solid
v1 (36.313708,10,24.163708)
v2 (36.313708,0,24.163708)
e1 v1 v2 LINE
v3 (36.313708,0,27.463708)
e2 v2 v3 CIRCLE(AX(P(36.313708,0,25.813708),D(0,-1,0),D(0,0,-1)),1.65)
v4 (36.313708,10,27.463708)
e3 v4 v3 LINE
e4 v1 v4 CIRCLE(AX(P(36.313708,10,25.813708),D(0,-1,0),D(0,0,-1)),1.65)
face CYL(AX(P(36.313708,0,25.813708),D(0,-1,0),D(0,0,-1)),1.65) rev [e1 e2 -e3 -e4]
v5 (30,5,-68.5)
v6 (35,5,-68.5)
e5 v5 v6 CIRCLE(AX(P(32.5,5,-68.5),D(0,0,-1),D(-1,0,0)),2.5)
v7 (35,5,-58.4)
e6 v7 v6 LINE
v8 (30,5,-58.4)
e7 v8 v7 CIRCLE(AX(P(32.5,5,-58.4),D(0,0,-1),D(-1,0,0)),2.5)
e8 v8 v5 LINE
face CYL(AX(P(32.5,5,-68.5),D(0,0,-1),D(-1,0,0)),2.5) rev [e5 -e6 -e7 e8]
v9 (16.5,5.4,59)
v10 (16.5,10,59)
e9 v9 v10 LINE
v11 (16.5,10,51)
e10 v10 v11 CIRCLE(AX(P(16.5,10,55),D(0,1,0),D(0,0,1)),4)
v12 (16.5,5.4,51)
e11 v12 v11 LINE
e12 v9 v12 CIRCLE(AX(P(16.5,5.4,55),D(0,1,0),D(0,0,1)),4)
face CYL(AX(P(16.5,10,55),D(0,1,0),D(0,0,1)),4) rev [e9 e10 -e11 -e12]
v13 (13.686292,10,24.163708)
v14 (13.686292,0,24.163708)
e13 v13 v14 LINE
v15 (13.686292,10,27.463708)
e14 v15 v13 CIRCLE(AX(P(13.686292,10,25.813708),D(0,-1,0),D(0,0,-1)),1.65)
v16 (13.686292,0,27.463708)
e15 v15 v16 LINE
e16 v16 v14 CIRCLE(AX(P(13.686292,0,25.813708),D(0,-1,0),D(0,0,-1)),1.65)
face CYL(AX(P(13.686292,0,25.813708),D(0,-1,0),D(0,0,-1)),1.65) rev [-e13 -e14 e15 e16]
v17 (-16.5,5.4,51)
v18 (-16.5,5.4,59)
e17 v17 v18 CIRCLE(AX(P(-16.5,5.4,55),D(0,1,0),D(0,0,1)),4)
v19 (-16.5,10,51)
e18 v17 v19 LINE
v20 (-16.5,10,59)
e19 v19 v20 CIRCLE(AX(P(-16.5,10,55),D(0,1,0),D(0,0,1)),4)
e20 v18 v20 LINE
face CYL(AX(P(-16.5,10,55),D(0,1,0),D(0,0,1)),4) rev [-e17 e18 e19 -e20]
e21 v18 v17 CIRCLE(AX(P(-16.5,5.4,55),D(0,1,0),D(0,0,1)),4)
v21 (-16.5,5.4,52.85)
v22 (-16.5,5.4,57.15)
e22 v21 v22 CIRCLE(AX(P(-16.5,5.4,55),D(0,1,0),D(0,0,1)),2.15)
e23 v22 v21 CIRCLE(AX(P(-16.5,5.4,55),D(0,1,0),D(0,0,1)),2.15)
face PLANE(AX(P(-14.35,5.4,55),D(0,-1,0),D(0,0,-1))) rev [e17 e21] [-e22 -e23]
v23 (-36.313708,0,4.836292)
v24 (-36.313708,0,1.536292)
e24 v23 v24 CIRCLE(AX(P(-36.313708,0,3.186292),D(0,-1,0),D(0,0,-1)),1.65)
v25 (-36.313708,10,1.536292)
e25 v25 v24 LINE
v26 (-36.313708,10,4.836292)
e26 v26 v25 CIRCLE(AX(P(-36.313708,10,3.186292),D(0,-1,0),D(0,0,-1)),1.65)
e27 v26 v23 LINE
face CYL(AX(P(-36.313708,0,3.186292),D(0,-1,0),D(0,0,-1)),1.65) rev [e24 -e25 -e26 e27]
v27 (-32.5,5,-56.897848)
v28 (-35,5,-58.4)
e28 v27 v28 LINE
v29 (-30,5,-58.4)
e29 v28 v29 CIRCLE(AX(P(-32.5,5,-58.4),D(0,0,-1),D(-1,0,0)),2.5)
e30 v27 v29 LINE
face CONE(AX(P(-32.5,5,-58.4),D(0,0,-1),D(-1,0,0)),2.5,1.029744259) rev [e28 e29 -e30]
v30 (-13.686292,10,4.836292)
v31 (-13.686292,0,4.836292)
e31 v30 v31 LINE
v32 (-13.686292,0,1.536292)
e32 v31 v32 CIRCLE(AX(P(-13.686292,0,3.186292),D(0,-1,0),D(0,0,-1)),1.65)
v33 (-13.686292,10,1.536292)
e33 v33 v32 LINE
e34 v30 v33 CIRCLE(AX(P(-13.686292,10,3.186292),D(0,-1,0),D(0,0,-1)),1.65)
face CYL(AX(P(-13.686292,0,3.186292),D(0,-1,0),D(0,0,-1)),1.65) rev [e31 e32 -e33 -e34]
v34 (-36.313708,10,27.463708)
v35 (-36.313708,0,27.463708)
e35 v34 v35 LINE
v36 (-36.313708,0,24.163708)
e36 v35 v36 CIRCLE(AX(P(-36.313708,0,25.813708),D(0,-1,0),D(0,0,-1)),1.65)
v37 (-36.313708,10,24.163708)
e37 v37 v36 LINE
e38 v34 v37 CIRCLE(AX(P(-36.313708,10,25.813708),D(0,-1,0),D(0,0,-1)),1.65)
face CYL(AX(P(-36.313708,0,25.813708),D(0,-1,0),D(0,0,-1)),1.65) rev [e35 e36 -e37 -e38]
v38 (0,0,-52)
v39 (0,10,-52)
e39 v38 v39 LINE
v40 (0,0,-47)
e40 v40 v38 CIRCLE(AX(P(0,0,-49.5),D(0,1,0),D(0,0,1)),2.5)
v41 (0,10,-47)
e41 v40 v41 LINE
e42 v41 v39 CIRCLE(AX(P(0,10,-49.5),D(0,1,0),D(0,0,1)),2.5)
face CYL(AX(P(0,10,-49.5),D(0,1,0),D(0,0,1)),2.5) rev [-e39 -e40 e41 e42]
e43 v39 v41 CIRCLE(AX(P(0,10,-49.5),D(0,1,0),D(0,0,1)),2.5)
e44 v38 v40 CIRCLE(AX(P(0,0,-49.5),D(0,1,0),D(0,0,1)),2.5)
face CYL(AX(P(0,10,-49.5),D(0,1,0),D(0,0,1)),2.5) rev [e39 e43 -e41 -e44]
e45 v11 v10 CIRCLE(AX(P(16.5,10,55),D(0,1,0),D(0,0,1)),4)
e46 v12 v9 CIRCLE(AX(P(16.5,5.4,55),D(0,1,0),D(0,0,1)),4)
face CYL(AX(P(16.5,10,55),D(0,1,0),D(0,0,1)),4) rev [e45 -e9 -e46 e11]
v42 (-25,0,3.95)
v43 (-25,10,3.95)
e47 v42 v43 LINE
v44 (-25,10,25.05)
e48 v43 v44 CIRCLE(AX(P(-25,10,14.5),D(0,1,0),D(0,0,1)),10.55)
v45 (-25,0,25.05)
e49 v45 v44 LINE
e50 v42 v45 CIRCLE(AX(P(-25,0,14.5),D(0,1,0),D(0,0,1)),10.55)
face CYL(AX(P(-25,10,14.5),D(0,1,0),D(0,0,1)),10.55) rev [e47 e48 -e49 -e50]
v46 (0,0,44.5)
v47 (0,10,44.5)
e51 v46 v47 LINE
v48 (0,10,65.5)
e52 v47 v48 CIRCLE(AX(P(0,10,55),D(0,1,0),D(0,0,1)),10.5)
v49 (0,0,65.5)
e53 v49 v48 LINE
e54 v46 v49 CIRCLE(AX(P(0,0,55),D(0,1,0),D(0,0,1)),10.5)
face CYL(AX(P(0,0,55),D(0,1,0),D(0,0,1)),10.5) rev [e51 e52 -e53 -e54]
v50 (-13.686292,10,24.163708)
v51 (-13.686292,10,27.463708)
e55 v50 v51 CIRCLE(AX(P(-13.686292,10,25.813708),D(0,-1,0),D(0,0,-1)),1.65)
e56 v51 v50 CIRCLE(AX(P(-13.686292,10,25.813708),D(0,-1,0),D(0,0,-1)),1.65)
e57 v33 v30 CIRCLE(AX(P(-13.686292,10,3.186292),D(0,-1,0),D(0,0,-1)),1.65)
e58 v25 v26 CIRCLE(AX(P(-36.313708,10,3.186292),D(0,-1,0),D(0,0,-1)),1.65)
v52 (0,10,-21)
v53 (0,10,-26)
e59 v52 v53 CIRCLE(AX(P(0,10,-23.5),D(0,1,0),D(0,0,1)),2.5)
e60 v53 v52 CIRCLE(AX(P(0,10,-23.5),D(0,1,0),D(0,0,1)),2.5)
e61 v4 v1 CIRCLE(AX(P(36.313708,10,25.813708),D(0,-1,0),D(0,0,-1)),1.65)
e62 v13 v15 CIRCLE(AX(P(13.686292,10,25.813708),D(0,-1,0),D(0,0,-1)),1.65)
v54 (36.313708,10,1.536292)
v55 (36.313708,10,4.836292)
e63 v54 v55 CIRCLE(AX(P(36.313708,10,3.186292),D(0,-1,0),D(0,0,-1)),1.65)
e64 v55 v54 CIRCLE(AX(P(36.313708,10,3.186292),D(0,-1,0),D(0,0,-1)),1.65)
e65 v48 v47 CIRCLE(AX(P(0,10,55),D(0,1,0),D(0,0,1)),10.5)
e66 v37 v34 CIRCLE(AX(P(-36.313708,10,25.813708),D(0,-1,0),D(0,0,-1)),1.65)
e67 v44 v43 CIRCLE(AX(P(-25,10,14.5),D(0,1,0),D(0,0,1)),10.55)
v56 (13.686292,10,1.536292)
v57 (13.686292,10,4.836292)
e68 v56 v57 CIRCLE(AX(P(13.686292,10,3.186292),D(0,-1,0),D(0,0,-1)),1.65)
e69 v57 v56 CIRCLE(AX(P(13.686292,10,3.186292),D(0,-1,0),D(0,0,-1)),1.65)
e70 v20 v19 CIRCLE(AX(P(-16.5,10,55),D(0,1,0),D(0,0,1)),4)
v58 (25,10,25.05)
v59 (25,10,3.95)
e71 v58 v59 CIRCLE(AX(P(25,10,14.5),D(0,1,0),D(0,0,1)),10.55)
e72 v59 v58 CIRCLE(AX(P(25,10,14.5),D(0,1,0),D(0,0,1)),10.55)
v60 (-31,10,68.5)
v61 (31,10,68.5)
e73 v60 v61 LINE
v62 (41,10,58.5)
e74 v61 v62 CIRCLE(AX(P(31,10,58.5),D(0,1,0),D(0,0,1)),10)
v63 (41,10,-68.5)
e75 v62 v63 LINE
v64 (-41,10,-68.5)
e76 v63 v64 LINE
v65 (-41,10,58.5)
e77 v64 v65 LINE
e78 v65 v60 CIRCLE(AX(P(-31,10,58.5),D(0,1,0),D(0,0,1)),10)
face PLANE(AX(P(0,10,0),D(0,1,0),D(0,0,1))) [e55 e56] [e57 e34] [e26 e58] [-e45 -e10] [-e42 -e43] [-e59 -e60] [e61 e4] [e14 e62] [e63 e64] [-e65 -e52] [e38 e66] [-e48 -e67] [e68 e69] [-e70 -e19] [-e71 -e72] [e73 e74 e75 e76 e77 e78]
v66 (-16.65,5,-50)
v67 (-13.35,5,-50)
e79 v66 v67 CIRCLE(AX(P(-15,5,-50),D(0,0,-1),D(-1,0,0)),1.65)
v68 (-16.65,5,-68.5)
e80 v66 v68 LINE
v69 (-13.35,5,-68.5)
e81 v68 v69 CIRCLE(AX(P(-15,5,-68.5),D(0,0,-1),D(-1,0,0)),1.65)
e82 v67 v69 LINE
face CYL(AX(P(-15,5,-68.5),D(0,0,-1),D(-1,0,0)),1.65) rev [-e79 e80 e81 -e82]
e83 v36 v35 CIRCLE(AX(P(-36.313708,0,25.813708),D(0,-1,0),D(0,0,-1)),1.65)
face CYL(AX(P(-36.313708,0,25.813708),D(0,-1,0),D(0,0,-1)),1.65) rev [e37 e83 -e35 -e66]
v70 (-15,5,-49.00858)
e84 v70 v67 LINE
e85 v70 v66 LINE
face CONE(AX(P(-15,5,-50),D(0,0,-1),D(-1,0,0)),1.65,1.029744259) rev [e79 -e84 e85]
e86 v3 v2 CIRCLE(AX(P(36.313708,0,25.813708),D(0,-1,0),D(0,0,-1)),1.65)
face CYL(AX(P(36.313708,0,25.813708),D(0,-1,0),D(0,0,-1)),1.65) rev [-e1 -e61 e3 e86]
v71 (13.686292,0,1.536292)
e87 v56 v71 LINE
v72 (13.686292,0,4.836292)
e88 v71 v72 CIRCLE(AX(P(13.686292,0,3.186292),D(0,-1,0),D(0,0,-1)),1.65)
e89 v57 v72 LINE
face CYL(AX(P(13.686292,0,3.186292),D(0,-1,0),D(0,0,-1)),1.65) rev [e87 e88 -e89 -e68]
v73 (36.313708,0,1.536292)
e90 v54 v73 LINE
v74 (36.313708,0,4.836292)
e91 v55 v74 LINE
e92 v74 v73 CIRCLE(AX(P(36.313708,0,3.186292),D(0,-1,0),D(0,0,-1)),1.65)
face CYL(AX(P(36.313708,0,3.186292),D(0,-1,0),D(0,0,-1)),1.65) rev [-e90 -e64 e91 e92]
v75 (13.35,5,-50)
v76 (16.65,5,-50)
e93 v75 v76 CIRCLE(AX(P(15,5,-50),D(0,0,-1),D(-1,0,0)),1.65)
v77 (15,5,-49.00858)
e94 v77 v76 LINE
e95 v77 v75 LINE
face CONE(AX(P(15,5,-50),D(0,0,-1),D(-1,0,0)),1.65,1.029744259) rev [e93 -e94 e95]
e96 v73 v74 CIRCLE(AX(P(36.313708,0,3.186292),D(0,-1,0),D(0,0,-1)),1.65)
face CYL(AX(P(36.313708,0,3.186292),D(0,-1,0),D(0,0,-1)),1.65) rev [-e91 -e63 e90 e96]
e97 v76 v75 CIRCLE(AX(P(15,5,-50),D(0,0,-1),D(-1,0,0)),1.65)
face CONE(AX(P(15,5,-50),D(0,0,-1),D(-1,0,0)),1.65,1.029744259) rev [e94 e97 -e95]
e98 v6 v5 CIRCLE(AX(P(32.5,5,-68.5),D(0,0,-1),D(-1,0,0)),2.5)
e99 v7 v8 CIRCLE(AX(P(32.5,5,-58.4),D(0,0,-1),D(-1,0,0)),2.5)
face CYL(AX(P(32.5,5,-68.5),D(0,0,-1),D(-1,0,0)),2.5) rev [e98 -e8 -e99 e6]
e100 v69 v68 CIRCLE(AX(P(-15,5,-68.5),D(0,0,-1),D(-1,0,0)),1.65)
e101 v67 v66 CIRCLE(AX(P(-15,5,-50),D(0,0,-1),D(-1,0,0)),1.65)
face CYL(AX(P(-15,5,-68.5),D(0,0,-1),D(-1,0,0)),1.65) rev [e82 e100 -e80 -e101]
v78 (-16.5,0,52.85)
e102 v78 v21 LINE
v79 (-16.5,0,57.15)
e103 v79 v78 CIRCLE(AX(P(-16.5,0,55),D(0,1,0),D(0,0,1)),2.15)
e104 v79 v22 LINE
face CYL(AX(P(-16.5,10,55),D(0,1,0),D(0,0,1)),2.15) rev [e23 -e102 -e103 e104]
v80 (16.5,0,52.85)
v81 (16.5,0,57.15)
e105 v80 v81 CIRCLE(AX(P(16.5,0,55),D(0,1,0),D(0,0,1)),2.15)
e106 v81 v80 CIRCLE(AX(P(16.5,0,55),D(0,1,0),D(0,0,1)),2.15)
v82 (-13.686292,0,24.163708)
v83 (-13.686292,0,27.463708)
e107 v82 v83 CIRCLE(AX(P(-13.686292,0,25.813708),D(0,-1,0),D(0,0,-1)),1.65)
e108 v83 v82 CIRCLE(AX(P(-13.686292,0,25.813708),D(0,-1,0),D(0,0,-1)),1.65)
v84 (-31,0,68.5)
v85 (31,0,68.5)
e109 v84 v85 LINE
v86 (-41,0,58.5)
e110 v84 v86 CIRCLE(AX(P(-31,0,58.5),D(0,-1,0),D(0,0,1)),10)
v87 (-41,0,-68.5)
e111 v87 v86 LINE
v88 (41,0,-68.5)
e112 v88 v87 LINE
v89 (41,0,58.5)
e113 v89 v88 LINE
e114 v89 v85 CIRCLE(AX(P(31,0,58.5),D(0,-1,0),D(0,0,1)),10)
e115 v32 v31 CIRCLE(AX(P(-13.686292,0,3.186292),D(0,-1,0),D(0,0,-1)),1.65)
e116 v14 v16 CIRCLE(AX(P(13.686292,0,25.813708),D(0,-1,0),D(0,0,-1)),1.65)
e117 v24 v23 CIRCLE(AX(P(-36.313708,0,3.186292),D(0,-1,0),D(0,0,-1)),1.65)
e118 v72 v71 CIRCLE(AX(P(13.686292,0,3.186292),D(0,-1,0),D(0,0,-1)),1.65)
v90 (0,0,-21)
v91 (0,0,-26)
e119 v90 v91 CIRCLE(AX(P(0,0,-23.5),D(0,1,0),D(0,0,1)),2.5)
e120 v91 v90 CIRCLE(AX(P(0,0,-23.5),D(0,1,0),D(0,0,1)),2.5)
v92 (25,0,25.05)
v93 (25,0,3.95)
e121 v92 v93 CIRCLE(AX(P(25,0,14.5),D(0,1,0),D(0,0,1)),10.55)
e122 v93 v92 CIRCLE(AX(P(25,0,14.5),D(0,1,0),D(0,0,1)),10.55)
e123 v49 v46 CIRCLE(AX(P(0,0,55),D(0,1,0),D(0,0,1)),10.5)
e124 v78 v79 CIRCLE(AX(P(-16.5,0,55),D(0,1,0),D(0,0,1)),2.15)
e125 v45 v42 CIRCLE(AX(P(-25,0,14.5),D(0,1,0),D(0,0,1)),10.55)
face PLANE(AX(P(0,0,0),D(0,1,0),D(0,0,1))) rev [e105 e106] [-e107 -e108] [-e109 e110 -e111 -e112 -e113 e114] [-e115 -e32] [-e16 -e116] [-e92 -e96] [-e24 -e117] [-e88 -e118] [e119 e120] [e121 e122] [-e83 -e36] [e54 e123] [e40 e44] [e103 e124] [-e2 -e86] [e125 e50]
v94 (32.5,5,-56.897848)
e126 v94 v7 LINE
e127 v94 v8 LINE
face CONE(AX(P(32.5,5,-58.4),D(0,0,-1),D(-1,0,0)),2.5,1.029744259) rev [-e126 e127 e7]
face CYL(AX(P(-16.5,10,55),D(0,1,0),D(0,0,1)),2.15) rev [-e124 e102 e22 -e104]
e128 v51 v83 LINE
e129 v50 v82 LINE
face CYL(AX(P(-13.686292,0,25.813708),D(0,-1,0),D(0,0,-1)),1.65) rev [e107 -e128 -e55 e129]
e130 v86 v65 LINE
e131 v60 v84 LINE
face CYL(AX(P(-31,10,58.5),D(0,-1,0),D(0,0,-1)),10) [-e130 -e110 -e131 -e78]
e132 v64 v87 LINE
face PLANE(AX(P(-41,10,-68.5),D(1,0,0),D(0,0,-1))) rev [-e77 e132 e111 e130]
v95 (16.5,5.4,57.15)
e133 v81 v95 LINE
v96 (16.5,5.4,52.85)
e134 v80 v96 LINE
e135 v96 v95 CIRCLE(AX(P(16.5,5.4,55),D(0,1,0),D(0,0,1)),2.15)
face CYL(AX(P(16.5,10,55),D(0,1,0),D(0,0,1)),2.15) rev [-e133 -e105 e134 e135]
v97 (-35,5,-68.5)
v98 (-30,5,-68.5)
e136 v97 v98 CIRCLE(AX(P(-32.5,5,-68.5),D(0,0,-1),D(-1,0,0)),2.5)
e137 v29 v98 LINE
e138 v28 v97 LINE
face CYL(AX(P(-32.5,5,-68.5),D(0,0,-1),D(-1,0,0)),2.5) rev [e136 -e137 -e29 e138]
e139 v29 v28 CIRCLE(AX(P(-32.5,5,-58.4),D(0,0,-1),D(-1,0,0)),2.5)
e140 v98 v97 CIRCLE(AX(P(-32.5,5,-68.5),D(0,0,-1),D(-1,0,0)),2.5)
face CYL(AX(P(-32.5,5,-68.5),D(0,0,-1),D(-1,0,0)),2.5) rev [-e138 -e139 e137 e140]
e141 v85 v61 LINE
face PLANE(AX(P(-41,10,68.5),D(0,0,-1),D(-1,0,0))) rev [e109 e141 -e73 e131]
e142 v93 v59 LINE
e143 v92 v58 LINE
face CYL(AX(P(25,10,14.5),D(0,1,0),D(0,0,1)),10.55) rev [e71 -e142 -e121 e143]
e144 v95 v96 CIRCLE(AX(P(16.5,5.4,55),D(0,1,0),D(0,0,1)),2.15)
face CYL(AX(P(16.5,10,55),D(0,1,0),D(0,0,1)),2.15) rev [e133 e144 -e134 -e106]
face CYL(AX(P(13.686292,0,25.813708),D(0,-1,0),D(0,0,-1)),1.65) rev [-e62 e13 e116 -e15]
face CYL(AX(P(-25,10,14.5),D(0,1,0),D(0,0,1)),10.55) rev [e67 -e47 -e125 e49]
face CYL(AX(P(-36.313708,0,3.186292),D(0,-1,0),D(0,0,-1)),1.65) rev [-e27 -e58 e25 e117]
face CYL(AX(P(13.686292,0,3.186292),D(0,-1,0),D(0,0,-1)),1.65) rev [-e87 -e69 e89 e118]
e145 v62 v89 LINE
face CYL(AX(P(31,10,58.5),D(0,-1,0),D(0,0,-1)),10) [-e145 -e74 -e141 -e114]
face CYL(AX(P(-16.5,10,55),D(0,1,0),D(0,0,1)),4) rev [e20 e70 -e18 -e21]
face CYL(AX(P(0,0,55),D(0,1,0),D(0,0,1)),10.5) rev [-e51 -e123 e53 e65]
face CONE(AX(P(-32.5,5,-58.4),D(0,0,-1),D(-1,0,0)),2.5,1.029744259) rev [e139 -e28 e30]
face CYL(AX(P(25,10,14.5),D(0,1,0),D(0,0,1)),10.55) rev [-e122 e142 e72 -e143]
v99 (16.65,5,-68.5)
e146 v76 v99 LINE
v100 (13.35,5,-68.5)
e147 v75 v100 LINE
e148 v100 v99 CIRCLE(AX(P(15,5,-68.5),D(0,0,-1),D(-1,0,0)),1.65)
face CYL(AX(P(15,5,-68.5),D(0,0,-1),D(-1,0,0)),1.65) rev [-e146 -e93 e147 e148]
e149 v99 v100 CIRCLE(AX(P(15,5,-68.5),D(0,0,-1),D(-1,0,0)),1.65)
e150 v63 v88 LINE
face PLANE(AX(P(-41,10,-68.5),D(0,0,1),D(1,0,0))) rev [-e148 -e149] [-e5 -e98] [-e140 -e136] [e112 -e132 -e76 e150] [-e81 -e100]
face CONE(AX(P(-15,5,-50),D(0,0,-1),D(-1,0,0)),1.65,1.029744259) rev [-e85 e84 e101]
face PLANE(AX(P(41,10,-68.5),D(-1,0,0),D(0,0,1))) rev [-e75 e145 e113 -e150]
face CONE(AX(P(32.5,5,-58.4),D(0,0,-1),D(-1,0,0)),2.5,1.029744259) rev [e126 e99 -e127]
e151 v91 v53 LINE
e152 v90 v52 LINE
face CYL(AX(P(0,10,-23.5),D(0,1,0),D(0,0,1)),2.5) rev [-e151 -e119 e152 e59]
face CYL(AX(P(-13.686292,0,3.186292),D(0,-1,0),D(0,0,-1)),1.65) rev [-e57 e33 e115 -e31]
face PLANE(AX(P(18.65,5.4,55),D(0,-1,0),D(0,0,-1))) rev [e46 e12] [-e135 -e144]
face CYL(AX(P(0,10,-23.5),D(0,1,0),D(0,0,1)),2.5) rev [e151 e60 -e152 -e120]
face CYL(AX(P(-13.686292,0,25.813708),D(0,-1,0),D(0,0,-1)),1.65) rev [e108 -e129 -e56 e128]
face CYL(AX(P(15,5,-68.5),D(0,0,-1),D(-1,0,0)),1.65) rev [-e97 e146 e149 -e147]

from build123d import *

# Parameters (mm, degrees)
SKETCH_1_W                = 82
SKETCH_1_H                = 137
EXTRUDE_1_DEPTH           = 10
SKETCH_4_R                = 10.5
CUT_EXTRUDE_3_DEPTH       = 81.456509991
FILLET_9_R                = 10
HOLE_WIZARD_2_D           = 4.3
HOLE_WIZARD_2_CBORE_D     = 8
HOLE_WIZARD_2_CBORE_DEPTH = 4.6
HOLE_WIZARD_M4_2_D        = 3.3
HOLE_WIZARD_M4_2_DEPTH    = 18.5
HOLE_WIZARD_M4_2_TIP      = 0.991420021
MM_2_D                    = 21.1
HOLE_WIZARD_M4_3_D        = 3.3
MM_2_2_D                  = 5
MM_2_2_DEPTH              = 10.1
MM_2_2_TIP                = 1.502151548
HOLE_WIZARD_M6_1_D        = 5
HOLE_WIZARD_M6_1_DEPTH    = 15
HOLE_WIZARD_M6_1_TIP      = 1.502151548
HOLE_WIZARD_M6_4_D        = 5


with BuildPart() as part:
    # 草图1 → 凸台-拉伸1 (new body)
    with BuildSketch(Plane(origin=(0, 0, 0), x_dir=(1, 0, 0), z_dir=(0, 1, 0))):
        Rectangle(SKETCH_1_W, SKETCH_1_H)
    extrude(amount=EXTRUDE_1_DEPTH)

    # 草图4 → 切除-拉伸3 (cut, through all)
    with BuildSketch(Plane(origin=(0, 10, 0), x_dir=(1, 0, 0), z_dir=(0, 1, 0))):
        with Locations(Location((0, -55, 0), (0, 0, 270))):
            Circle(SKETCH_4_R)
    extrude(amount=-CUT_EXTRUDE_3_DEPTH, mode=Mode.SUBTRACT)

    # 圆角9
    fillet_9_edges = [part.edges().sort_by_distance(p)[0] for p in [
        (41, 5, 68.5),
        (-41, 5, 68.5),
    ]]
    fillet(fillet_9_edges, radius=FILLET_9_R)

    # 打孔尺寸(%根据)开槽圆柱头螺钉的类型2 (through all)
    with Locations(Plane(origin=(0, 10, 0), x_dir=(1, 0, 0), z_dir=(0, 1, 0))):
        with Locations((-16.5, -55), (16.5, -55)):
            CounterBoreHole(HOLE_WIZARD_2_D / 2, HOLE_WIZARD_2_CBORE_D / 2, HOLE_WIZARD_2_CBORE_DEPTH)

    # M4 螺纹孔2
    with Locations(Plane(origin=(0, 0, -68.5), x_dir=(-1, 0, 0), z_dir=(0, 0, -1))):
        with Locations((-15, 5), (15, 5)):
            Hole(HOLE_WIZARD_M4_2_D / 2, depth=HOLE_WIZARD_M4_2_DEPTH)
            with Locations((0, 0, -(HOLE_WIZARD_M4_2_DEPTH + HOLE_WIZARD_M4_2_TIP / 2))):  # 118° drill point
                Cone(0, HOLE_WIZARD_M4_2_D / 2, HOLE_WIZARD_M4_2_TIP, mode=Mode.SUBTRACT)

    # mm _2 (through all)
    with Locations(Plane(origin=(0, 10, 0), x_dir=(1, 0, 0), z_dir=(0, 1, 0))):
        with Locations((-25, -14.5), (25, -14.5)):
            Hole(MM_2_D / 2)

    # M4 螺纹孔3 (through all)
    with Locations(Plane(origin=(0, 0, 0), x_dir=(-1, 0, 0), z_dir=(0, -1, 0))):
        with Locations((-13.686291501, -3.186291501), (-36.313708499, -3.186291501), (-36.313708499, -25.813708499), (-13.686291501, -25.813708499)):
            hole_wizard_m4_3 = Hole(HOLE_WIZARD_M4_3_D / 2)

    # 镜向2: M4 螺纹孔3 across plane
    add(hole_wizard_m4_3.mirror(Plane(origin=(0, 0, 0), x_dir=(0, 0, 1), z_dir=(1, 0, 0))), mode=Mode.SUBTRACT)

    # mm _2 2
    with Locations(Plane(origin=(0, 0, -68.5), x_dir=(-1, 0, 0), z_dir=(0, 0, -1))):
        with Locations((32.5, 5), (-32.5, 5)):
            Hole(MM_2_2_D / 2, depth=MM_2_2_DEPTH)
            with Locations((0, 0, -(MM_2_2_DEPTH + MM_2_2_TIP / 2))):  # 118° drill point
                Cone(0, MM_2_2_D / 2, MM_2_2_TIP, mode=Mode.SUBTRACT)

    # M6 螺纹孔1
    with Locations(Plane(origin=(0, 10, 0), x_dir=(1, 0, 0), z_dir=(0, 1, 0))):
        with Locations((0, 49.5)):
            Hole(HOLE_WIZARD_M6_1_D / 2, depth=HOLE_WIZARD_M6_1_DEPTH)
            with Locations((0, 0, -(HOLE_WIZARD_M6_1_DEPTH + HOLE_WIZARD_M6_1_TIP / 2))):  # 118° drill point
                Cone(0, HOLE_WIZARD_M6_1_D / 2, HOLE_WIZARD_M6_1_TIP, mode=Mode.SUBTRACT)

    # M6 螺纹孔4 (through all)
    with Locations(Plane(origin=(0, 10, 0), x_dir=(1, 0, 0), z_dir=(0, 1, 0))):
        with Locations((0, 23.5)):
            Hole(HOLE_WIZARD_M6_4_D / 2)


solid = part.part
